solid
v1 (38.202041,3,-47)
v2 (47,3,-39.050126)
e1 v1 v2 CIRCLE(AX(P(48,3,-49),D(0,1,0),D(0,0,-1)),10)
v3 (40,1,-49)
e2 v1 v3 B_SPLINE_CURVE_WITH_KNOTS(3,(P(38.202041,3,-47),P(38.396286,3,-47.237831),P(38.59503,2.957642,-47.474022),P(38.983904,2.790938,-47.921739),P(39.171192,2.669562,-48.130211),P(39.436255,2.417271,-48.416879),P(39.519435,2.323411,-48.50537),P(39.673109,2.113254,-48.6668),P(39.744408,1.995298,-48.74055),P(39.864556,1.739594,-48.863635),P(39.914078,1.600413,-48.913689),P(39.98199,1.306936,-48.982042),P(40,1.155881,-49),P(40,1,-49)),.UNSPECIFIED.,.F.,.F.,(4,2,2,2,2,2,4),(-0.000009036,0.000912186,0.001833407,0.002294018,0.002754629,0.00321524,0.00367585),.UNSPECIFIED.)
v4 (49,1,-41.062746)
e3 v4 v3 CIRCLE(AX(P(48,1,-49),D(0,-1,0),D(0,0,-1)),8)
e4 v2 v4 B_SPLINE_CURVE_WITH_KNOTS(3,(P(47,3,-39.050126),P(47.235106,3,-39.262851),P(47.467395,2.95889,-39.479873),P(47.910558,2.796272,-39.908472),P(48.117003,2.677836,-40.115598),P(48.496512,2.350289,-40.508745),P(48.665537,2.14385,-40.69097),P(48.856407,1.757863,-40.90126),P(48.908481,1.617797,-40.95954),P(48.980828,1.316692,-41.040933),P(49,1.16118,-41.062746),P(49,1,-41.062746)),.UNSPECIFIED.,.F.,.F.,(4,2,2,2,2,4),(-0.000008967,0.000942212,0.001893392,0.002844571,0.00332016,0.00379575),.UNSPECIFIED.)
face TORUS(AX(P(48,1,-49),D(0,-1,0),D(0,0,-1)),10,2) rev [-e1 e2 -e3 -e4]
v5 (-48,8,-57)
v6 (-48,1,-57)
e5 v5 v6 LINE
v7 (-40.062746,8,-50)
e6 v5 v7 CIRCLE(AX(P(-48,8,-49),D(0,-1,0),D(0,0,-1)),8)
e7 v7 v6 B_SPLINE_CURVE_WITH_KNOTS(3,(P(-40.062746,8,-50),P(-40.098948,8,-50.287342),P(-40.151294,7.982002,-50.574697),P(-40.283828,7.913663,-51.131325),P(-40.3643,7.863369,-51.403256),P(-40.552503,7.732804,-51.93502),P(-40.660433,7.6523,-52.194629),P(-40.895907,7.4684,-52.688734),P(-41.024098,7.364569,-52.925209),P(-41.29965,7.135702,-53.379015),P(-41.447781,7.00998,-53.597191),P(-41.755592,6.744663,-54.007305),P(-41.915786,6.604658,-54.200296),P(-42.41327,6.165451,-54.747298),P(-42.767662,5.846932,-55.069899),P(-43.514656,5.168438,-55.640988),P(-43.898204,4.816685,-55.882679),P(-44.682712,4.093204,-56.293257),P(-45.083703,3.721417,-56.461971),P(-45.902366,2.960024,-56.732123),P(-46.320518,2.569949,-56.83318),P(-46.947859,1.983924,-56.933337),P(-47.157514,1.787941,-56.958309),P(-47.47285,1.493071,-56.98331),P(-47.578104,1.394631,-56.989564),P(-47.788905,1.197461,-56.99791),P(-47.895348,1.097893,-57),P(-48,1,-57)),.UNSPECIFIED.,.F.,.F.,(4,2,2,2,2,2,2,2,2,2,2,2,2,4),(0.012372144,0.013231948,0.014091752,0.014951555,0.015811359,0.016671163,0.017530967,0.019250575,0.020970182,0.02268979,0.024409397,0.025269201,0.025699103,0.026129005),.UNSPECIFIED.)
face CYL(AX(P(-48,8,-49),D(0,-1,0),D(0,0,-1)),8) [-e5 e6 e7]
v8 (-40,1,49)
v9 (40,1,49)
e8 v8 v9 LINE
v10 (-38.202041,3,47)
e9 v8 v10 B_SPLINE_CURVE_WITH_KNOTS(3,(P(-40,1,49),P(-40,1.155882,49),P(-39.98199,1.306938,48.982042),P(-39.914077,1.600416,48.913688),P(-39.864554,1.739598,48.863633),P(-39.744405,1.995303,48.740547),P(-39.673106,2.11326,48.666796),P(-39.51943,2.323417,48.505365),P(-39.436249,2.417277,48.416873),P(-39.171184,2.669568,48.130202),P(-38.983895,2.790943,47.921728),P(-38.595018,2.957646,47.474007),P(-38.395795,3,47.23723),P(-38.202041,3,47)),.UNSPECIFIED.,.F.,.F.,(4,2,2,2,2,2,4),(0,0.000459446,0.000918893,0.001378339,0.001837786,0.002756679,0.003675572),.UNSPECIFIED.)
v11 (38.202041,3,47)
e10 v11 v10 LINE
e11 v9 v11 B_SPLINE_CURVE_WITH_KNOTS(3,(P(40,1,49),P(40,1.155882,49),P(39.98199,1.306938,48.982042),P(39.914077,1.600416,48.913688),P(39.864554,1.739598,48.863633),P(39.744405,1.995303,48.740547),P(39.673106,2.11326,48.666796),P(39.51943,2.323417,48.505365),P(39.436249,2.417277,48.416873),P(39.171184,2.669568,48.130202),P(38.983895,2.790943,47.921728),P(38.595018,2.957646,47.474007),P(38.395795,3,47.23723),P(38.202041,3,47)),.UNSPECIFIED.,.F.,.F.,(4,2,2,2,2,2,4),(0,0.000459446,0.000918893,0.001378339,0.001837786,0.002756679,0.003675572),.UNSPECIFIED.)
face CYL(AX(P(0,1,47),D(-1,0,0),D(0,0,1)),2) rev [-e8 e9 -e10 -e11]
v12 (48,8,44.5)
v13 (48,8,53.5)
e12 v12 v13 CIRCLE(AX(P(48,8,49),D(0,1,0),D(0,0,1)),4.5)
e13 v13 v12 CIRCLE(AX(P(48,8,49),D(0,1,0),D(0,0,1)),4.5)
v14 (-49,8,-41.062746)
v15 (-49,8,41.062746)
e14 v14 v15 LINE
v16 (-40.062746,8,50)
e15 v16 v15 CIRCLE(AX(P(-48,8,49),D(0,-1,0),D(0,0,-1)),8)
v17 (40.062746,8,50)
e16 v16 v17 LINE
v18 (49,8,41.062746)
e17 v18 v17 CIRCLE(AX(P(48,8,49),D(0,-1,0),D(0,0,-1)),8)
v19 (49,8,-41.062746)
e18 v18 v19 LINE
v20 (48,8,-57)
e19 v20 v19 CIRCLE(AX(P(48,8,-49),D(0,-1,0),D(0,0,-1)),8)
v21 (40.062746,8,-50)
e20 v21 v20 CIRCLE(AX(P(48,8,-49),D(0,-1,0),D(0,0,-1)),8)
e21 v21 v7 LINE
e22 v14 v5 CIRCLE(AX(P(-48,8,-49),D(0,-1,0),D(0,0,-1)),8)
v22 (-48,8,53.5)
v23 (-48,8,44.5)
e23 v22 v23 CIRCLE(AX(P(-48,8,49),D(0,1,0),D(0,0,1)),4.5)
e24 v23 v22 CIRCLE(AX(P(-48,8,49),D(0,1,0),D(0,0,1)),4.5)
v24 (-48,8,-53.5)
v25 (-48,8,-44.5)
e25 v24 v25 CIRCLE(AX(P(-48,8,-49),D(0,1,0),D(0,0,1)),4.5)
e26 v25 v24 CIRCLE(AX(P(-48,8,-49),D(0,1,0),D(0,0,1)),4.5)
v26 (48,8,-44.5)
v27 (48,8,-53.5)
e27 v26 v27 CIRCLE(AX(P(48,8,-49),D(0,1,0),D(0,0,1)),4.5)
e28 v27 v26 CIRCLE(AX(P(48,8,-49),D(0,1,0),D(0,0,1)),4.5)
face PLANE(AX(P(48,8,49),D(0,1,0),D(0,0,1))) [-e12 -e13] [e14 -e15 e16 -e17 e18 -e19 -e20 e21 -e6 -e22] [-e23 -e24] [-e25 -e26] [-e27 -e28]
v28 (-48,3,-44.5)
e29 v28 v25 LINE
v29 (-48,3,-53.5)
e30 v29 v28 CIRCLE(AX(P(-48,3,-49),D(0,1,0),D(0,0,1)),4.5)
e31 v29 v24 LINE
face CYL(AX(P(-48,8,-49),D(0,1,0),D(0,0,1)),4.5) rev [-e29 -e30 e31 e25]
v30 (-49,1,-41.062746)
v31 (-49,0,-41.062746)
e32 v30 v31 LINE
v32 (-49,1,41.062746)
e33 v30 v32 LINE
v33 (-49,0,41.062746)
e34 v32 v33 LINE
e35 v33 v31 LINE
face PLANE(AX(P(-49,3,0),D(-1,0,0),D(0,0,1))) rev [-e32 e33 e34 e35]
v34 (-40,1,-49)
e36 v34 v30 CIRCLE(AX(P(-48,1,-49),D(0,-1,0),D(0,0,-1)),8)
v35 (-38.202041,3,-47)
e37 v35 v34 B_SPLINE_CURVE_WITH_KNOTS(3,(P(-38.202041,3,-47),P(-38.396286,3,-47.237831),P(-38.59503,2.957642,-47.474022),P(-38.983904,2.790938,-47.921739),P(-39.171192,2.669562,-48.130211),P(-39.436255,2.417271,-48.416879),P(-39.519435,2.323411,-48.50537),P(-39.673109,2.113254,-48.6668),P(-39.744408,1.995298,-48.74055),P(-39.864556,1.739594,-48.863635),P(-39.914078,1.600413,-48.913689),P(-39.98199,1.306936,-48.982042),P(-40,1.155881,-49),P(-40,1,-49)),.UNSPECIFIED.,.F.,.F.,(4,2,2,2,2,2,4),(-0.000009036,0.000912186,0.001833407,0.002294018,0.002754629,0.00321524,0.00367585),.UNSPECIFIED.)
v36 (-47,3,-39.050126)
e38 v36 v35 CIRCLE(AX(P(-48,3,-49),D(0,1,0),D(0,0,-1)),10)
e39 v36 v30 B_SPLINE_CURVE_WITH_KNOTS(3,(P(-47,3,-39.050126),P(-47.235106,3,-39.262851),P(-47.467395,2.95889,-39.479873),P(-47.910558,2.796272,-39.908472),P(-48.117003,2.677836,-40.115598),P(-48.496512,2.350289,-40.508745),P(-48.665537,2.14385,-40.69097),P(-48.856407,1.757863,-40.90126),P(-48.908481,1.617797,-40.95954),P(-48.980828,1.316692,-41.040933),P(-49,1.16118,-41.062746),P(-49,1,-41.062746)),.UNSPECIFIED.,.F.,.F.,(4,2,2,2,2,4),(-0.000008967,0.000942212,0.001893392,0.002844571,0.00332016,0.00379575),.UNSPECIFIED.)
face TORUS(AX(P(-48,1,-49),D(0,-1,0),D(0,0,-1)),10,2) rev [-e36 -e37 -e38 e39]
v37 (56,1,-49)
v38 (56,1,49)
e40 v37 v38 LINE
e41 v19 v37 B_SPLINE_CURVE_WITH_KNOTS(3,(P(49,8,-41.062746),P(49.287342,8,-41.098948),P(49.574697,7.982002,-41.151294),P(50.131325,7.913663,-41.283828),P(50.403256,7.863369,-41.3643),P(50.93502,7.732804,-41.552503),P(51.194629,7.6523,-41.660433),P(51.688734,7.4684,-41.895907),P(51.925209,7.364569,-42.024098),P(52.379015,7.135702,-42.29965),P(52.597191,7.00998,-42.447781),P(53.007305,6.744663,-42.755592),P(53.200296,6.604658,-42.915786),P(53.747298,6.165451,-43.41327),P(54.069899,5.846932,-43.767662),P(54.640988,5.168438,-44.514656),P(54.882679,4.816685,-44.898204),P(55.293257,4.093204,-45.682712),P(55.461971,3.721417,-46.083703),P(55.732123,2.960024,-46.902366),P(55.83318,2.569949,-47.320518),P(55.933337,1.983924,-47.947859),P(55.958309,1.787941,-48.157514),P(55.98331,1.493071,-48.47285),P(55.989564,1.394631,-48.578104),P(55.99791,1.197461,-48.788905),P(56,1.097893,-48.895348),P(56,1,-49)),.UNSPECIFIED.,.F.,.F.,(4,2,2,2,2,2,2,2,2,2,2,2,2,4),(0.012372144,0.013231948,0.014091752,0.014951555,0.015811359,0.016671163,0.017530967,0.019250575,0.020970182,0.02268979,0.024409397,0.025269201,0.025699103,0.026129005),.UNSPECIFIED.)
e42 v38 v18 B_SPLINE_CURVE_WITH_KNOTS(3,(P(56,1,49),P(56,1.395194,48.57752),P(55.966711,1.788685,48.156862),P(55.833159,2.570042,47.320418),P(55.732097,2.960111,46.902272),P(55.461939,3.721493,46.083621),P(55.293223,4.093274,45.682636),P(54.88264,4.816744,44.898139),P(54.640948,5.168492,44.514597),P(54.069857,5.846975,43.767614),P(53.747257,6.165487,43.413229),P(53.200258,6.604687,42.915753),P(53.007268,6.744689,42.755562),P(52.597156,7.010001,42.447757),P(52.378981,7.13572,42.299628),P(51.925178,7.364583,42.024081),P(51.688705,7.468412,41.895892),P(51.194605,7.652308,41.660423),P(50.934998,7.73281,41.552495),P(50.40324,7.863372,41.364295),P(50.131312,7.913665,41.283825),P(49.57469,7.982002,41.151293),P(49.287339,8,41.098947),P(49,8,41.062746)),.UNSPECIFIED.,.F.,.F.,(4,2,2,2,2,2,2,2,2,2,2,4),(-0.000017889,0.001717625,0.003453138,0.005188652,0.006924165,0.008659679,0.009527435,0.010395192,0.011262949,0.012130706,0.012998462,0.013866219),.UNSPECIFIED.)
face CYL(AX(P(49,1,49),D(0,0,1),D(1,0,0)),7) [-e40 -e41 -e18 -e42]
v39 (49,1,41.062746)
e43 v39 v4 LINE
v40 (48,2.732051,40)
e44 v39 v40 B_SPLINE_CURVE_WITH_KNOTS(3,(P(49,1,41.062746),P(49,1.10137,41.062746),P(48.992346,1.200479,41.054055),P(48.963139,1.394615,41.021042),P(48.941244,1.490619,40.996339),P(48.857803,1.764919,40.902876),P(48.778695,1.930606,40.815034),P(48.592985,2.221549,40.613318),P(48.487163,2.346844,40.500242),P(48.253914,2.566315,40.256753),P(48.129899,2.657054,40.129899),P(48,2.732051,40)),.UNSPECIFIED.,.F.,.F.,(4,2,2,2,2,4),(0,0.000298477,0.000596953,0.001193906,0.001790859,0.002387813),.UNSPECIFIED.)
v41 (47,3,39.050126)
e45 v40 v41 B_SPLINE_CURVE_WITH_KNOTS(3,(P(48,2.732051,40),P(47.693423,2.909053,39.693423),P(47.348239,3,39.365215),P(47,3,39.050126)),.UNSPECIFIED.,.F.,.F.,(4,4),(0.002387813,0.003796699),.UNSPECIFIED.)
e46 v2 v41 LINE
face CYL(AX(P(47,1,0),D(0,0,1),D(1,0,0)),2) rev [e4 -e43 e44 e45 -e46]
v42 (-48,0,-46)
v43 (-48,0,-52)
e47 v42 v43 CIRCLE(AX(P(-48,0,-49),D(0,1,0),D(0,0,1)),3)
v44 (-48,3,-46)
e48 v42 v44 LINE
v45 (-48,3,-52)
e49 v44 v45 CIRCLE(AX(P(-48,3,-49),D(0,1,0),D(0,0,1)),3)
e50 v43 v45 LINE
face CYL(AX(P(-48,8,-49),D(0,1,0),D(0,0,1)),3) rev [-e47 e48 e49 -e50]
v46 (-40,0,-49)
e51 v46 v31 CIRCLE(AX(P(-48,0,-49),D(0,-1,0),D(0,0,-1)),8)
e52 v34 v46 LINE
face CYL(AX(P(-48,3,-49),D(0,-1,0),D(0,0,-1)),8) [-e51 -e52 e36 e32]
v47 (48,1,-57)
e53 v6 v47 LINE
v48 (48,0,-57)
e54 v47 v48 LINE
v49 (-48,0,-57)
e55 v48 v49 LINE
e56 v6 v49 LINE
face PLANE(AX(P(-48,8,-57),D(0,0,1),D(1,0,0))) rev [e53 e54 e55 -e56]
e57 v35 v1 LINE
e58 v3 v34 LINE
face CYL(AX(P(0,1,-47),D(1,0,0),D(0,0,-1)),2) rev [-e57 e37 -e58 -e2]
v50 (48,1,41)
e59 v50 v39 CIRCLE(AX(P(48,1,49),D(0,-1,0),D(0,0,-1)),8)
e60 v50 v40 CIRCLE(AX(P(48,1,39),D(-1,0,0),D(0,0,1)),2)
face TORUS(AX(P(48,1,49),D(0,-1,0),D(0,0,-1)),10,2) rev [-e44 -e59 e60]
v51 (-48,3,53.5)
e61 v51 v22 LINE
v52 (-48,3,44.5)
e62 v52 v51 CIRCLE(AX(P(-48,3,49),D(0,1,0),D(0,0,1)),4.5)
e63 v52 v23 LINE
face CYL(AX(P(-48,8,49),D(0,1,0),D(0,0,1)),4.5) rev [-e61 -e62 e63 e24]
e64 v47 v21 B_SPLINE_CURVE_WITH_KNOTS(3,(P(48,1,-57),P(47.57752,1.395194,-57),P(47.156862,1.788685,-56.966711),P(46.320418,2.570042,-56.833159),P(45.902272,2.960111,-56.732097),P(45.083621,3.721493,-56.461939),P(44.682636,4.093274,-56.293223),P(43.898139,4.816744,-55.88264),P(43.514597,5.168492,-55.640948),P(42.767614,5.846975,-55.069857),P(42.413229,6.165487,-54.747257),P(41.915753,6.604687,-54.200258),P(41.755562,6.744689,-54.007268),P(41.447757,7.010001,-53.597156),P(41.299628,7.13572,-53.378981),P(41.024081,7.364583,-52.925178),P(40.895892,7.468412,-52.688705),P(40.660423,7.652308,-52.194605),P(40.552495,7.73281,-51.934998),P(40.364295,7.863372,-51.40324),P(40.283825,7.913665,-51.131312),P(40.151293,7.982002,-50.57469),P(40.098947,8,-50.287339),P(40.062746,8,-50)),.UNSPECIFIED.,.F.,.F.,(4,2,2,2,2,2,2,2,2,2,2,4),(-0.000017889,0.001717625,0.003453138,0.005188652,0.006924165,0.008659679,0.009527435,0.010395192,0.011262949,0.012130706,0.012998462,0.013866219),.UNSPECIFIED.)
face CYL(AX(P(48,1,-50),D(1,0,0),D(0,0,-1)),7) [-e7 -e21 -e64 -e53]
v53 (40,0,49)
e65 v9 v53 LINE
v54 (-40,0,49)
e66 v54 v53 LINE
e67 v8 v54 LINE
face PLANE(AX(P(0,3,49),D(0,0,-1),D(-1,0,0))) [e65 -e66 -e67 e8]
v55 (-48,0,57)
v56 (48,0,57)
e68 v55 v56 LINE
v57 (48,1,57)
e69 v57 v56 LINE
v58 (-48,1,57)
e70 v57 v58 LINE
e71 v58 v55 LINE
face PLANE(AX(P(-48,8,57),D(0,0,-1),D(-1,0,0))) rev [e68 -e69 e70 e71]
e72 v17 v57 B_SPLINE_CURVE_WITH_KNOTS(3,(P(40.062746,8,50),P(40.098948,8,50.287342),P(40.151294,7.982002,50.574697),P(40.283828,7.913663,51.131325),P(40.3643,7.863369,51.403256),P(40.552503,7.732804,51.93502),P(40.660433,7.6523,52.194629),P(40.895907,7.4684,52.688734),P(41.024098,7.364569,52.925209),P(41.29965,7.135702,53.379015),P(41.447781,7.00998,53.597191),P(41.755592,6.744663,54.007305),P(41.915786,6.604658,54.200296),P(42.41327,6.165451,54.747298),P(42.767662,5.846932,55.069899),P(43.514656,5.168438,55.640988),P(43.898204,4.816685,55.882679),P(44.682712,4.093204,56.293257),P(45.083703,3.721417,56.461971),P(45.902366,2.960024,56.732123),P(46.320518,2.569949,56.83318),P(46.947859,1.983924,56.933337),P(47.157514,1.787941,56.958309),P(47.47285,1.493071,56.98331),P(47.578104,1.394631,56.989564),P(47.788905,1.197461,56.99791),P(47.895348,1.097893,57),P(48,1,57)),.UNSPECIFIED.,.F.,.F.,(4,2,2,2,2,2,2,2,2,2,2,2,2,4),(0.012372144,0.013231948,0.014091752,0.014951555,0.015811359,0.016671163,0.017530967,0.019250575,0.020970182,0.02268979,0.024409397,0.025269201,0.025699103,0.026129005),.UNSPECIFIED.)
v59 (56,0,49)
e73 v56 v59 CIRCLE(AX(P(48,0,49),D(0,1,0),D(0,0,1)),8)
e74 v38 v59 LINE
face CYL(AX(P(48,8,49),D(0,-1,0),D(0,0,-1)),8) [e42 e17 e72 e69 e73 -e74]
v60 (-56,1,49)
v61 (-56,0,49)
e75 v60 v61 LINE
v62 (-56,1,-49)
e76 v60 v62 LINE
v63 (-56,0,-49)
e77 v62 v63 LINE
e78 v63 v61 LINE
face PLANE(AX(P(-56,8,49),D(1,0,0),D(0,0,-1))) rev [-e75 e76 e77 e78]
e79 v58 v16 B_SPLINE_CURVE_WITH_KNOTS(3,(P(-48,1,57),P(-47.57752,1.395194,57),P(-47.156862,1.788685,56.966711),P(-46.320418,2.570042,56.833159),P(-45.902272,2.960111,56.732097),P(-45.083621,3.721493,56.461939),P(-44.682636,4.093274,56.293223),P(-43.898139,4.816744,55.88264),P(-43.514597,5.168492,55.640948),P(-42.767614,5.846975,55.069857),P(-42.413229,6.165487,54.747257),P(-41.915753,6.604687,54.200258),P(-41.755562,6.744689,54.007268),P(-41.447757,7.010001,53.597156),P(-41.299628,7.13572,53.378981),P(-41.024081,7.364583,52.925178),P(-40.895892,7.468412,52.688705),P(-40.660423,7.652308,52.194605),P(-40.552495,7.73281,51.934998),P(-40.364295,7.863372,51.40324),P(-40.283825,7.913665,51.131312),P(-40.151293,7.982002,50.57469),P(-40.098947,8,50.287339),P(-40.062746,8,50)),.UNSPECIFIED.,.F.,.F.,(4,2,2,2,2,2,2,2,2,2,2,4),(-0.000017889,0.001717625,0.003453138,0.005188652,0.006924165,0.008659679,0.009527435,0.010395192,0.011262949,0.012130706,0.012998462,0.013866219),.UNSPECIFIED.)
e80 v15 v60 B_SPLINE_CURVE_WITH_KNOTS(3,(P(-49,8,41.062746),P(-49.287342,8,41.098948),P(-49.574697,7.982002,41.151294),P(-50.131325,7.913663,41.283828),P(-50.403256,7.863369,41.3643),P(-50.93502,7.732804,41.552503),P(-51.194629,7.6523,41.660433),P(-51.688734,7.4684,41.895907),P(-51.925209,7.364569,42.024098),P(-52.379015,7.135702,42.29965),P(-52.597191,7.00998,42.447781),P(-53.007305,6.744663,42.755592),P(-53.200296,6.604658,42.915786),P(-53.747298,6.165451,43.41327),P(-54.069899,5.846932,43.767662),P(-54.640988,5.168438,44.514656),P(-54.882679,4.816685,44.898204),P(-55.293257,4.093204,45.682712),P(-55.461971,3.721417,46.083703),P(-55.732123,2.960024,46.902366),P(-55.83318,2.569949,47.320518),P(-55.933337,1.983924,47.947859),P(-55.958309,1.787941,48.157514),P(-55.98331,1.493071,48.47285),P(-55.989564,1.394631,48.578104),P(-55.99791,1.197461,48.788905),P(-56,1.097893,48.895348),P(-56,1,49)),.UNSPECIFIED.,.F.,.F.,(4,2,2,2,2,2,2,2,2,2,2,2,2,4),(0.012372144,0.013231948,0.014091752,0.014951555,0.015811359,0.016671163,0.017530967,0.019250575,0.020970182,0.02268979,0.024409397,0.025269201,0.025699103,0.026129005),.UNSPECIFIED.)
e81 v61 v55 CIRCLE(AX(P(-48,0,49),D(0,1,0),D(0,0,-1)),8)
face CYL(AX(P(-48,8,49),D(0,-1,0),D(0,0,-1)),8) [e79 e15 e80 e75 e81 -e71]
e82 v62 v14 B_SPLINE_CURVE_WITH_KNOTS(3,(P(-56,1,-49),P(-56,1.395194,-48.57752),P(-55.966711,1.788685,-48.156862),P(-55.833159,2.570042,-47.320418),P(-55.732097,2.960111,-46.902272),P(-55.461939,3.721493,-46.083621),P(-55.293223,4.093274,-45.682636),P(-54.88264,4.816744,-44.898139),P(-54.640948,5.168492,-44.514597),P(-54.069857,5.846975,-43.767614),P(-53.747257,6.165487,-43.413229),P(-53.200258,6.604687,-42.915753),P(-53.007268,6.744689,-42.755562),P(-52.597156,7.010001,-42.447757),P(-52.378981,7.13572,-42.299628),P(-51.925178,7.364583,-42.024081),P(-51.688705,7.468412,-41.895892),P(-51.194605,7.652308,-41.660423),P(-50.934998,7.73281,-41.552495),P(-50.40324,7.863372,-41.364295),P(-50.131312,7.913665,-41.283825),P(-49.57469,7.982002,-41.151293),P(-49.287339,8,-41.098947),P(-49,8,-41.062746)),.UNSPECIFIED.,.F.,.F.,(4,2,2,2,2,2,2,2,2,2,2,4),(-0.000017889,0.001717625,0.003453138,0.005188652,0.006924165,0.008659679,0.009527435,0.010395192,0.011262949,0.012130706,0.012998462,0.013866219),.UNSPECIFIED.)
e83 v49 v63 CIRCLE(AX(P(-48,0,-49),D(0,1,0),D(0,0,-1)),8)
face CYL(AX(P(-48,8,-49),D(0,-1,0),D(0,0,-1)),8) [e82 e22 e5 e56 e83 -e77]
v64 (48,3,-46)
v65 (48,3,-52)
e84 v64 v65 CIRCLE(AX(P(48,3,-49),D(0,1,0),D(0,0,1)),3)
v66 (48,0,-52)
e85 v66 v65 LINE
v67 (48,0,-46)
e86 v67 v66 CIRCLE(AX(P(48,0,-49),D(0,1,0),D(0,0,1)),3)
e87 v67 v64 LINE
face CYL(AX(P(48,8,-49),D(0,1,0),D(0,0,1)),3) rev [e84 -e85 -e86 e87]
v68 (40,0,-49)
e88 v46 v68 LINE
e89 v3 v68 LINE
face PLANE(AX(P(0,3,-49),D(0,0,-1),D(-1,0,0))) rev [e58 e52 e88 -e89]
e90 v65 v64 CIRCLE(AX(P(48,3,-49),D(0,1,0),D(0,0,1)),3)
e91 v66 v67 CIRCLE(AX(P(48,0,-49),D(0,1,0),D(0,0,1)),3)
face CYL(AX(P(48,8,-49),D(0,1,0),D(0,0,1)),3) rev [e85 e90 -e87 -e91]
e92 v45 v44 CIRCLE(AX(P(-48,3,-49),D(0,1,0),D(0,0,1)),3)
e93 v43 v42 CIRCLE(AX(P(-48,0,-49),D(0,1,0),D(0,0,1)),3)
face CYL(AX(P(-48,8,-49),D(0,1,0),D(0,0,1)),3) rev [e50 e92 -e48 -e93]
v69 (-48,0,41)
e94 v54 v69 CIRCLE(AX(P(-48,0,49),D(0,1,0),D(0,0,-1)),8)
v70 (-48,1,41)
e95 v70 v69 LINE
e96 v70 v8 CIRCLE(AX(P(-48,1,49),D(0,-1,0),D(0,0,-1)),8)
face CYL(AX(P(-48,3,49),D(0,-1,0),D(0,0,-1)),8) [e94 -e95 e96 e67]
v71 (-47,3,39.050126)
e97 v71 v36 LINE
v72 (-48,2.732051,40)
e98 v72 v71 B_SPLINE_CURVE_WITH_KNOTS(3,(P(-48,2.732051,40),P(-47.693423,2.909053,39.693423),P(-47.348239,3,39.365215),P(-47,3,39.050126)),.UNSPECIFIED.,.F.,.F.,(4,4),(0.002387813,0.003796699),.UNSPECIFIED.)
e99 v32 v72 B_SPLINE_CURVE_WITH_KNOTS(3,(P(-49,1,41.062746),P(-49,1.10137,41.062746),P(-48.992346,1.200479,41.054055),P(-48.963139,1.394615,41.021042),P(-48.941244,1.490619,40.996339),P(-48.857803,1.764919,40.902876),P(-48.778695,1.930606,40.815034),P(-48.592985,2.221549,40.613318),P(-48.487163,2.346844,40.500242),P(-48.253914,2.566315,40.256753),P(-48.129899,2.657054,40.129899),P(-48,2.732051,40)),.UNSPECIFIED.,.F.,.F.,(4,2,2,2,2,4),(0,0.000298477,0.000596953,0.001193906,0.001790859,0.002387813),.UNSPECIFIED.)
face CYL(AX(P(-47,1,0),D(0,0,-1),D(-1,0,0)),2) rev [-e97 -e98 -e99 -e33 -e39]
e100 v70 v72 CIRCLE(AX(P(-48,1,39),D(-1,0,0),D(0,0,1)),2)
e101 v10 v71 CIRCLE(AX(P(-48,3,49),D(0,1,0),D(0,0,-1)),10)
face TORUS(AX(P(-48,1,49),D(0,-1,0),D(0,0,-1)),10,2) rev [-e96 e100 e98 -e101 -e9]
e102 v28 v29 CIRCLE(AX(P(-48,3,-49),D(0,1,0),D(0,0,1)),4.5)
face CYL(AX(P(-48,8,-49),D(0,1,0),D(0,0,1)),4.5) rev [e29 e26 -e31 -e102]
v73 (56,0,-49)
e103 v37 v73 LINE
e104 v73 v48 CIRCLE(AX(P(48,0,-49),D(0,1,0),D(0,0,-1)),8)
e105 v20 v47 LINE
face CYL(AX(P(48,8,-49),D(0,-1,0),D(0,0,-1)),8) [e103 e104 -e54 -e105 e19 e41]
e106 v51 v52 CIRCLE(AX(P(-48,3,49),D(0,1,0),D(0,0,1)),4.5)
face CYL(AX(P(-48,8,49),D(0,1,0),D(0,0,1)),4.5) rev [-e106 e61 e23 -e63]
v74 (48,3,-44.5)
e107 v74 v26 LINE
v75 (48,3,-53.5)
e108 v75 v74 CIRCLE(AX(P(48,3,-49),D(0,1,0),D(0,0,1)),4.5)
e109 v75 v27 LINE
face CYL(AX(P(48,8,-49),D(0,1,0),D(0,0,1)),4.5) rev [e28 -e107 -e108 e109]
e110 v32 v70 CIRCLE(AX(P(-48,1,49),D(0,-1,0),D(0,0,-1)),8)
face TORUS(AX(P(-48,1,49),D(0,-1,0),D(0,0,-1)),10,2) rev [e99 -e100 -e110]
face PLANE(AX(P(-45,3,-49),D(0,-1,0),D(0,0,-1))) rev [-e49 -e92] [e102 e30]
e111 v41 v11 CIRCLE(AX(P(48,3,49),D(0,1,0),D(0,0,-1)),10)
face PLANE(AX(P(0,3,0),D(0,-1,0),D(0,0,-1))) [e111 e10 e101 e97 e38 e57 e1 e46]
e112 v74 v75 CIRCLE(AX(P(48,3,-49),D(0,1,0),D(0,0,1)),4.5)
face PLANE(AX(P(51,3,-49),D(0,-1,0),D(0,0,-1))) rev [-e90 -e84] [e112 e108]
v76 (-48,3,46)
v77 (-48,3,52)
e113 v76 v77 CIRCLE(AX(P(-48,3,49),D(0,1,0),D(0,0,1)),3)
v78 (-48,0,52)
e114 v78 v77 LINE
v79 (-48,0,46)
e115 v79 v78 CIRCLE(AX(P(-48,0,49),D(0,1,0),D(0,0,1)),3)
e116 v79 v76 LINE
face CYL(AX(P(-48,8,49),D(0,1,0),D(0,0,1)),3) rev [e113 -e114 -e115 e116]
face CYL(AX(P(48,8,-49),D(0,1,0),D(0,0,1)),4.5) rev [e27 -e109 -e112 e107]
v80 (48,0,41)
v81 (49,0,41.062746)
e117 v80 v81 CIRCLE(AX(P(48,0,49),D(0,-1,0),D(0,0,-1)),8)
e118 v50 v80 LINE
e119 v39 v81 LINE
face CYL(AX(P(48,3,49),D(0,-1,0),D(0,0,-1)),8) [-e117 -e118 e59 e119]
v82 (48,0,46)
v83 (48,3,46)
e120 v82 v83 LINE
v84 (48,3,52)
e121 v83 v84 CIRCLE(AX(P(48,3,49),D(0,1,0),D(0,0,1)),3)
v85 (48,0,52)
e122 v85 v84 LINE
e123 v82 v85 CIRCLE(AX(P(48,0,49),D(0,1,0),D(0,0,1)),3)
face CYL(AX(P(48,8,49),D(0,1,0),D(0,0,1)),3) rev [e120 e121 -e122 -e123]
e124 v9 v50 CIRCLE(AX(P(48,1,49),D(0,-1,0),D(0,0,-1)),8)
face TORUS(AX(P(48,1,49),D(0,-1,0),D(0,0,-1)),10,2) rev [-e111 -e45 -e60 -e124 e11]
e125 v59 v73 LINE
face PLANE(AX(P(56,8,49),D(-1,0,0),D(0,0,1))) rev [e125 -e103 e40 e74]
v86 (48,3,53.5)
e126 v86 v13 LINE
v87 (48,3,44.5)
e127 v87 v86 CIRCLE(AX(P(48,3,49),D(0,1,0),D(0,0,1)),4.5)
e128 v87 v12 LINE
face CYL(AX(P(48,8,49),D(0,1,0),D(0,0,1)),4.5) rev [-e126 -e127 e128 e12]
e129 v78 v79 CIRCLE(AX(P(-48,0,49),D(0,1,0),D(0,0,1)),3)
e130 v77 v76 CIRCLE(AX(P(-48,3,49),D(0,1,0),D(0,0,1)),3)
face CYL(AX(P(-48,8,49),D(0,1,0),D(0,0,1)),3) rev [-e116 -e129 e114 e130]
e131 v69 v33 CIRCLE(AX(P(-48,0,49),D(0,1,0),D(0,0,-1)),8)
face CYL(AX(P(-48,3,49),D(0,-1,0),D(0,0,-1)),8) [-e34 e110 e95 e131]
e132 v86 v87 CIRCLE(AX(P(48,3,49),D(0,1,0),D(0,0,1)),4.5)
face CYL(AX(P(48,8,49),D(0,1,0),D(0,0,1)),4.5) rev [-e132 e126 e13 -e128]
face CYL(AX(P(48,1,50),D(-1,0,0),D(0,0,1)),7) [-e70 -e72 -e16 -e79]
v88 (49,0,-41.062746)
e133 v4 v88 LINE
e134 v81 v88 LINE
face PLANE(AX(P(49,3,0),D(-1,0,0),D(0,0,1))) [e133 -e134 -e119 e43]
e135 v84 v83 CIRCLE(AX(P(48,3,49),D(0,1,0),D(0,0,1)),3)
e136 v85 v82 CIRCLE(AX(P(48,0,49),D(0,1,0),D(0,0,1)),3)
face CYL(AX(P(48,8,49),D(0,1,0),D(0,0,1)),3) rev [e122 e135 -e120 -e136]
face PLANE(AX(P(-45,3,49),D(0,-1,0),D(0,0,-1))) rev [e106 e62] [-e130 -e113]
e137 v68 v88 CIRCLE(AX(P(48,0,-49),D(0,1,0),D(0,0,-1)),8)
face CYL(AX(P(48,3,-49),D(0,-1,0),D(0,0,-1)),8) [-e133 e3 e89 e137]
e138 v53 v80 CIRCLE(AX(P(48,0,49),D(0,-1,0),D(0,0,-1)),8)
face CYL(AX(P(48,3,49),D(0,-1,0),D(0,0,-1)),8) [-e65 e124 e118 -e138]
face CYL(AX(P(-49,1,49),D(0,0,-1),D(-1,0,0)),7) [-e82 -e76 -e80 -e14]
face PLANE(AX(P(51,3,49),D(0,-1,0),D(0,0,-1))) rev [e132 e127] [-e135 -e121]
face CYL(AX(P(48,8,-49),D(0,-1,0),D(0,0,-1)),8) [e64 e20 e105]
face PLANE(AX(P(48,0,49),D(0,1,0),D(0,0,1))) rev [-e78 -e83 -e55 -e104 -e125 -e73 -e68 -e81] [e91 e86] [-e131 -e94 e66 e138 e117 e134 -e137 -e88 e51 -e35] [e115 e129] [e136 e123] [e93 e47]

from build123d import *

# Parameters (mm, degrees)
BOSS_EXTRUDE1_DEPTH = 8
FILLET4_R           = 7
SKETCH2_R           = 7.999999999999998
SKETCH2_R_2         = 8.000000000000005
BOSS_EXTRUDE2_DEPTH = 8
CUT_EXTRUDE1_DEPTH  = 3
FILLET3_R           = 2
HOLE2_D             = 6
HOLE2_DEPTH         = 100
HOLE2_CBORE_D       = 9
HOLE2_CBORE_DEPTH   = 5


with BuildPart() as part:
    # Sketch1 → Boss-Extrude1 (new body)
    with BuildSketch(Plane(origin=(0, 0, 0), x_dir=(1, 0, 0), z_dir=(0, 1, 0))):
        with BuildLine():
            Line((-47.99999999999995, -57), (47.999999999999936, -57.000000000000014))
            ThreePointArc((47.999999999999936, -57.000000000000014), (53.656854249492376, -54.6568542494924), (55.99999999999999, -48.99999999999996))
            Line((55.99999999999999, -48.99999999999996), (56, 48.99999999999994))
            ThreePointArc((56, 48.99999999999994), (53.65685424949238, 54.65685424949238), (47.99999999999994, 57))
            Line((47.99999999999994, 57), (-47.99999999999996, 57))
            ThreePointArc((-47.99999999999996, 57), (-53.6568542494924, 54.65685424949238), (-56.000000000000014, 48.99999999999994))
            Line((-56.000000000000014, 48.99999999999994), (-56.00000000000001, -48.99999999999994))
            ThreePointArc((-56.00000000000001, -48.99999999999994), (-53.65685424949238, -54.65685424949238), (-47.99999999999995, -57))
        make_face()
    extrude(amount=BOSS_EXTRUDE1_DEPTH)

    # Fillet4
    fillet4_edges = [part.edges().sort_by_distance(p)[0] for p in [
        (53.65685424949238, 8, -54.65685424949238),
        (-7.11e-15, 8, -57),
        (-53.6568542494924, 8, -54.65685424949238),
        (-56.000000000000014, 8, 0),
        (-53.65685424949239, 8, 54.65685424949238),
        (-7.11e-15, 8, 57.00000000000001),
        (53.656854249492376, 8, 54.6568542494924),
        (55.99999999999999, 8, 7.11e-15),
    ]]
    fillet(fillet4_edges, radius=FILLET4_R)

    # Sketch2 → Boss-Extrude2 (add)
    with BuildSketch(Plane(origin=(0, 0, 0), x_dir=(-1, 0, 0), z_dir=(0, -1, 0))):
        with Locations((48.00000000000001, -49)):
            Circle(SKETCH2_R)
        with Locations((-47.99999999999999, -49.000000000000014)):
            Circle(SKETCH2_R_2)
        with Locations((-48, 49)):
            Circle(SKETCH2_R_2)
        with Locations((48.000000000000014, 49)):
            Circle(SKETCH2_R)
    extrude(amount=-BOSS_EXTRUDE2_DEPTH)

    # Sketch6 → Cut-Extrude1 (cut)
    with BuildSketch(Plane(origin=(0, 0, 0), x_dir=(-1, 0, 0), z_dir=(0, -1, 0))):
        with BuildLine():
            ThreePointArc((-48.99999999999984, -41.06274606680613), (-42.708497377870756, -42.99999999999998), (-40, -48.99999999999992))
            Line((-40.00000000000001, -49), (40.00000000000001, -49))
            ThreePointArc((40.00000000000001, -48.99999999999994), (42.70849737787087, -42.9999999999999), (49.00000000000012, -41.06274606680618))
            Line((48.99999999999999, -41.0627460668062), (48.99999999999999, 41.062746066806255))
            ThreePointArc((49.000000000000114, 41.062746066806234), (42.70849737787086, 42.999999999999964), (40.00000000000001, 49))
            Line((40.00000000000001, 49.00000000000001), (-39.999999999999936, 49.00000000000001))
            ThreePointArc((-39.999999999999936, 49.00000000000003), (-42.70849737787072, 43.00000000000006), (-48.99999999999983, 41.06274606680624))
            Line((-48.99999999999999, 41.06274606680623), (-48.99999999999999, -41.062746066806106))
        make_face()
    extrude(amount=-CUT_EXTRUDE1_DEPTH, mode=Mode.SUBTRACT)

    # Fillet3
    fillet3_edges = [part.edges().sort_by_distance(p)[0] for p in [
        (42.708497377870714, 3, -43.000000000000064),
        (-3.553e-14, 3, -49.00000000000001),
        (-48.99999999999999, 3, -2.842e-14),
        (-42.70849737787087, 3, 42.9999999999999),
        (42.708497377870756, 3, 42.99999999999998),
        (48.99999999999999, 3, -5.684e-14),
        (-42.70849737787086, 3, -42.99999999999996),
        (0, 3, 49),
    ]]
    fillet(fillet3_edges, radius=FILLET3_R)

    # Hole2
    with Locations(Plane(origin=(0, 8, 0), x_dir=(1, 0, 0), z_dir=(0, 1, 0))):
        with Locations((-48, 49), (48, 49), (-48, -49), (48, -49)):
            CounterBoreHole(HOLE2_D / 2, HOLE2_CBORE_D / 2, HOLE2_CBORE_DEPTH, depth=HOLE2_DEPTH)


solid = part.part
